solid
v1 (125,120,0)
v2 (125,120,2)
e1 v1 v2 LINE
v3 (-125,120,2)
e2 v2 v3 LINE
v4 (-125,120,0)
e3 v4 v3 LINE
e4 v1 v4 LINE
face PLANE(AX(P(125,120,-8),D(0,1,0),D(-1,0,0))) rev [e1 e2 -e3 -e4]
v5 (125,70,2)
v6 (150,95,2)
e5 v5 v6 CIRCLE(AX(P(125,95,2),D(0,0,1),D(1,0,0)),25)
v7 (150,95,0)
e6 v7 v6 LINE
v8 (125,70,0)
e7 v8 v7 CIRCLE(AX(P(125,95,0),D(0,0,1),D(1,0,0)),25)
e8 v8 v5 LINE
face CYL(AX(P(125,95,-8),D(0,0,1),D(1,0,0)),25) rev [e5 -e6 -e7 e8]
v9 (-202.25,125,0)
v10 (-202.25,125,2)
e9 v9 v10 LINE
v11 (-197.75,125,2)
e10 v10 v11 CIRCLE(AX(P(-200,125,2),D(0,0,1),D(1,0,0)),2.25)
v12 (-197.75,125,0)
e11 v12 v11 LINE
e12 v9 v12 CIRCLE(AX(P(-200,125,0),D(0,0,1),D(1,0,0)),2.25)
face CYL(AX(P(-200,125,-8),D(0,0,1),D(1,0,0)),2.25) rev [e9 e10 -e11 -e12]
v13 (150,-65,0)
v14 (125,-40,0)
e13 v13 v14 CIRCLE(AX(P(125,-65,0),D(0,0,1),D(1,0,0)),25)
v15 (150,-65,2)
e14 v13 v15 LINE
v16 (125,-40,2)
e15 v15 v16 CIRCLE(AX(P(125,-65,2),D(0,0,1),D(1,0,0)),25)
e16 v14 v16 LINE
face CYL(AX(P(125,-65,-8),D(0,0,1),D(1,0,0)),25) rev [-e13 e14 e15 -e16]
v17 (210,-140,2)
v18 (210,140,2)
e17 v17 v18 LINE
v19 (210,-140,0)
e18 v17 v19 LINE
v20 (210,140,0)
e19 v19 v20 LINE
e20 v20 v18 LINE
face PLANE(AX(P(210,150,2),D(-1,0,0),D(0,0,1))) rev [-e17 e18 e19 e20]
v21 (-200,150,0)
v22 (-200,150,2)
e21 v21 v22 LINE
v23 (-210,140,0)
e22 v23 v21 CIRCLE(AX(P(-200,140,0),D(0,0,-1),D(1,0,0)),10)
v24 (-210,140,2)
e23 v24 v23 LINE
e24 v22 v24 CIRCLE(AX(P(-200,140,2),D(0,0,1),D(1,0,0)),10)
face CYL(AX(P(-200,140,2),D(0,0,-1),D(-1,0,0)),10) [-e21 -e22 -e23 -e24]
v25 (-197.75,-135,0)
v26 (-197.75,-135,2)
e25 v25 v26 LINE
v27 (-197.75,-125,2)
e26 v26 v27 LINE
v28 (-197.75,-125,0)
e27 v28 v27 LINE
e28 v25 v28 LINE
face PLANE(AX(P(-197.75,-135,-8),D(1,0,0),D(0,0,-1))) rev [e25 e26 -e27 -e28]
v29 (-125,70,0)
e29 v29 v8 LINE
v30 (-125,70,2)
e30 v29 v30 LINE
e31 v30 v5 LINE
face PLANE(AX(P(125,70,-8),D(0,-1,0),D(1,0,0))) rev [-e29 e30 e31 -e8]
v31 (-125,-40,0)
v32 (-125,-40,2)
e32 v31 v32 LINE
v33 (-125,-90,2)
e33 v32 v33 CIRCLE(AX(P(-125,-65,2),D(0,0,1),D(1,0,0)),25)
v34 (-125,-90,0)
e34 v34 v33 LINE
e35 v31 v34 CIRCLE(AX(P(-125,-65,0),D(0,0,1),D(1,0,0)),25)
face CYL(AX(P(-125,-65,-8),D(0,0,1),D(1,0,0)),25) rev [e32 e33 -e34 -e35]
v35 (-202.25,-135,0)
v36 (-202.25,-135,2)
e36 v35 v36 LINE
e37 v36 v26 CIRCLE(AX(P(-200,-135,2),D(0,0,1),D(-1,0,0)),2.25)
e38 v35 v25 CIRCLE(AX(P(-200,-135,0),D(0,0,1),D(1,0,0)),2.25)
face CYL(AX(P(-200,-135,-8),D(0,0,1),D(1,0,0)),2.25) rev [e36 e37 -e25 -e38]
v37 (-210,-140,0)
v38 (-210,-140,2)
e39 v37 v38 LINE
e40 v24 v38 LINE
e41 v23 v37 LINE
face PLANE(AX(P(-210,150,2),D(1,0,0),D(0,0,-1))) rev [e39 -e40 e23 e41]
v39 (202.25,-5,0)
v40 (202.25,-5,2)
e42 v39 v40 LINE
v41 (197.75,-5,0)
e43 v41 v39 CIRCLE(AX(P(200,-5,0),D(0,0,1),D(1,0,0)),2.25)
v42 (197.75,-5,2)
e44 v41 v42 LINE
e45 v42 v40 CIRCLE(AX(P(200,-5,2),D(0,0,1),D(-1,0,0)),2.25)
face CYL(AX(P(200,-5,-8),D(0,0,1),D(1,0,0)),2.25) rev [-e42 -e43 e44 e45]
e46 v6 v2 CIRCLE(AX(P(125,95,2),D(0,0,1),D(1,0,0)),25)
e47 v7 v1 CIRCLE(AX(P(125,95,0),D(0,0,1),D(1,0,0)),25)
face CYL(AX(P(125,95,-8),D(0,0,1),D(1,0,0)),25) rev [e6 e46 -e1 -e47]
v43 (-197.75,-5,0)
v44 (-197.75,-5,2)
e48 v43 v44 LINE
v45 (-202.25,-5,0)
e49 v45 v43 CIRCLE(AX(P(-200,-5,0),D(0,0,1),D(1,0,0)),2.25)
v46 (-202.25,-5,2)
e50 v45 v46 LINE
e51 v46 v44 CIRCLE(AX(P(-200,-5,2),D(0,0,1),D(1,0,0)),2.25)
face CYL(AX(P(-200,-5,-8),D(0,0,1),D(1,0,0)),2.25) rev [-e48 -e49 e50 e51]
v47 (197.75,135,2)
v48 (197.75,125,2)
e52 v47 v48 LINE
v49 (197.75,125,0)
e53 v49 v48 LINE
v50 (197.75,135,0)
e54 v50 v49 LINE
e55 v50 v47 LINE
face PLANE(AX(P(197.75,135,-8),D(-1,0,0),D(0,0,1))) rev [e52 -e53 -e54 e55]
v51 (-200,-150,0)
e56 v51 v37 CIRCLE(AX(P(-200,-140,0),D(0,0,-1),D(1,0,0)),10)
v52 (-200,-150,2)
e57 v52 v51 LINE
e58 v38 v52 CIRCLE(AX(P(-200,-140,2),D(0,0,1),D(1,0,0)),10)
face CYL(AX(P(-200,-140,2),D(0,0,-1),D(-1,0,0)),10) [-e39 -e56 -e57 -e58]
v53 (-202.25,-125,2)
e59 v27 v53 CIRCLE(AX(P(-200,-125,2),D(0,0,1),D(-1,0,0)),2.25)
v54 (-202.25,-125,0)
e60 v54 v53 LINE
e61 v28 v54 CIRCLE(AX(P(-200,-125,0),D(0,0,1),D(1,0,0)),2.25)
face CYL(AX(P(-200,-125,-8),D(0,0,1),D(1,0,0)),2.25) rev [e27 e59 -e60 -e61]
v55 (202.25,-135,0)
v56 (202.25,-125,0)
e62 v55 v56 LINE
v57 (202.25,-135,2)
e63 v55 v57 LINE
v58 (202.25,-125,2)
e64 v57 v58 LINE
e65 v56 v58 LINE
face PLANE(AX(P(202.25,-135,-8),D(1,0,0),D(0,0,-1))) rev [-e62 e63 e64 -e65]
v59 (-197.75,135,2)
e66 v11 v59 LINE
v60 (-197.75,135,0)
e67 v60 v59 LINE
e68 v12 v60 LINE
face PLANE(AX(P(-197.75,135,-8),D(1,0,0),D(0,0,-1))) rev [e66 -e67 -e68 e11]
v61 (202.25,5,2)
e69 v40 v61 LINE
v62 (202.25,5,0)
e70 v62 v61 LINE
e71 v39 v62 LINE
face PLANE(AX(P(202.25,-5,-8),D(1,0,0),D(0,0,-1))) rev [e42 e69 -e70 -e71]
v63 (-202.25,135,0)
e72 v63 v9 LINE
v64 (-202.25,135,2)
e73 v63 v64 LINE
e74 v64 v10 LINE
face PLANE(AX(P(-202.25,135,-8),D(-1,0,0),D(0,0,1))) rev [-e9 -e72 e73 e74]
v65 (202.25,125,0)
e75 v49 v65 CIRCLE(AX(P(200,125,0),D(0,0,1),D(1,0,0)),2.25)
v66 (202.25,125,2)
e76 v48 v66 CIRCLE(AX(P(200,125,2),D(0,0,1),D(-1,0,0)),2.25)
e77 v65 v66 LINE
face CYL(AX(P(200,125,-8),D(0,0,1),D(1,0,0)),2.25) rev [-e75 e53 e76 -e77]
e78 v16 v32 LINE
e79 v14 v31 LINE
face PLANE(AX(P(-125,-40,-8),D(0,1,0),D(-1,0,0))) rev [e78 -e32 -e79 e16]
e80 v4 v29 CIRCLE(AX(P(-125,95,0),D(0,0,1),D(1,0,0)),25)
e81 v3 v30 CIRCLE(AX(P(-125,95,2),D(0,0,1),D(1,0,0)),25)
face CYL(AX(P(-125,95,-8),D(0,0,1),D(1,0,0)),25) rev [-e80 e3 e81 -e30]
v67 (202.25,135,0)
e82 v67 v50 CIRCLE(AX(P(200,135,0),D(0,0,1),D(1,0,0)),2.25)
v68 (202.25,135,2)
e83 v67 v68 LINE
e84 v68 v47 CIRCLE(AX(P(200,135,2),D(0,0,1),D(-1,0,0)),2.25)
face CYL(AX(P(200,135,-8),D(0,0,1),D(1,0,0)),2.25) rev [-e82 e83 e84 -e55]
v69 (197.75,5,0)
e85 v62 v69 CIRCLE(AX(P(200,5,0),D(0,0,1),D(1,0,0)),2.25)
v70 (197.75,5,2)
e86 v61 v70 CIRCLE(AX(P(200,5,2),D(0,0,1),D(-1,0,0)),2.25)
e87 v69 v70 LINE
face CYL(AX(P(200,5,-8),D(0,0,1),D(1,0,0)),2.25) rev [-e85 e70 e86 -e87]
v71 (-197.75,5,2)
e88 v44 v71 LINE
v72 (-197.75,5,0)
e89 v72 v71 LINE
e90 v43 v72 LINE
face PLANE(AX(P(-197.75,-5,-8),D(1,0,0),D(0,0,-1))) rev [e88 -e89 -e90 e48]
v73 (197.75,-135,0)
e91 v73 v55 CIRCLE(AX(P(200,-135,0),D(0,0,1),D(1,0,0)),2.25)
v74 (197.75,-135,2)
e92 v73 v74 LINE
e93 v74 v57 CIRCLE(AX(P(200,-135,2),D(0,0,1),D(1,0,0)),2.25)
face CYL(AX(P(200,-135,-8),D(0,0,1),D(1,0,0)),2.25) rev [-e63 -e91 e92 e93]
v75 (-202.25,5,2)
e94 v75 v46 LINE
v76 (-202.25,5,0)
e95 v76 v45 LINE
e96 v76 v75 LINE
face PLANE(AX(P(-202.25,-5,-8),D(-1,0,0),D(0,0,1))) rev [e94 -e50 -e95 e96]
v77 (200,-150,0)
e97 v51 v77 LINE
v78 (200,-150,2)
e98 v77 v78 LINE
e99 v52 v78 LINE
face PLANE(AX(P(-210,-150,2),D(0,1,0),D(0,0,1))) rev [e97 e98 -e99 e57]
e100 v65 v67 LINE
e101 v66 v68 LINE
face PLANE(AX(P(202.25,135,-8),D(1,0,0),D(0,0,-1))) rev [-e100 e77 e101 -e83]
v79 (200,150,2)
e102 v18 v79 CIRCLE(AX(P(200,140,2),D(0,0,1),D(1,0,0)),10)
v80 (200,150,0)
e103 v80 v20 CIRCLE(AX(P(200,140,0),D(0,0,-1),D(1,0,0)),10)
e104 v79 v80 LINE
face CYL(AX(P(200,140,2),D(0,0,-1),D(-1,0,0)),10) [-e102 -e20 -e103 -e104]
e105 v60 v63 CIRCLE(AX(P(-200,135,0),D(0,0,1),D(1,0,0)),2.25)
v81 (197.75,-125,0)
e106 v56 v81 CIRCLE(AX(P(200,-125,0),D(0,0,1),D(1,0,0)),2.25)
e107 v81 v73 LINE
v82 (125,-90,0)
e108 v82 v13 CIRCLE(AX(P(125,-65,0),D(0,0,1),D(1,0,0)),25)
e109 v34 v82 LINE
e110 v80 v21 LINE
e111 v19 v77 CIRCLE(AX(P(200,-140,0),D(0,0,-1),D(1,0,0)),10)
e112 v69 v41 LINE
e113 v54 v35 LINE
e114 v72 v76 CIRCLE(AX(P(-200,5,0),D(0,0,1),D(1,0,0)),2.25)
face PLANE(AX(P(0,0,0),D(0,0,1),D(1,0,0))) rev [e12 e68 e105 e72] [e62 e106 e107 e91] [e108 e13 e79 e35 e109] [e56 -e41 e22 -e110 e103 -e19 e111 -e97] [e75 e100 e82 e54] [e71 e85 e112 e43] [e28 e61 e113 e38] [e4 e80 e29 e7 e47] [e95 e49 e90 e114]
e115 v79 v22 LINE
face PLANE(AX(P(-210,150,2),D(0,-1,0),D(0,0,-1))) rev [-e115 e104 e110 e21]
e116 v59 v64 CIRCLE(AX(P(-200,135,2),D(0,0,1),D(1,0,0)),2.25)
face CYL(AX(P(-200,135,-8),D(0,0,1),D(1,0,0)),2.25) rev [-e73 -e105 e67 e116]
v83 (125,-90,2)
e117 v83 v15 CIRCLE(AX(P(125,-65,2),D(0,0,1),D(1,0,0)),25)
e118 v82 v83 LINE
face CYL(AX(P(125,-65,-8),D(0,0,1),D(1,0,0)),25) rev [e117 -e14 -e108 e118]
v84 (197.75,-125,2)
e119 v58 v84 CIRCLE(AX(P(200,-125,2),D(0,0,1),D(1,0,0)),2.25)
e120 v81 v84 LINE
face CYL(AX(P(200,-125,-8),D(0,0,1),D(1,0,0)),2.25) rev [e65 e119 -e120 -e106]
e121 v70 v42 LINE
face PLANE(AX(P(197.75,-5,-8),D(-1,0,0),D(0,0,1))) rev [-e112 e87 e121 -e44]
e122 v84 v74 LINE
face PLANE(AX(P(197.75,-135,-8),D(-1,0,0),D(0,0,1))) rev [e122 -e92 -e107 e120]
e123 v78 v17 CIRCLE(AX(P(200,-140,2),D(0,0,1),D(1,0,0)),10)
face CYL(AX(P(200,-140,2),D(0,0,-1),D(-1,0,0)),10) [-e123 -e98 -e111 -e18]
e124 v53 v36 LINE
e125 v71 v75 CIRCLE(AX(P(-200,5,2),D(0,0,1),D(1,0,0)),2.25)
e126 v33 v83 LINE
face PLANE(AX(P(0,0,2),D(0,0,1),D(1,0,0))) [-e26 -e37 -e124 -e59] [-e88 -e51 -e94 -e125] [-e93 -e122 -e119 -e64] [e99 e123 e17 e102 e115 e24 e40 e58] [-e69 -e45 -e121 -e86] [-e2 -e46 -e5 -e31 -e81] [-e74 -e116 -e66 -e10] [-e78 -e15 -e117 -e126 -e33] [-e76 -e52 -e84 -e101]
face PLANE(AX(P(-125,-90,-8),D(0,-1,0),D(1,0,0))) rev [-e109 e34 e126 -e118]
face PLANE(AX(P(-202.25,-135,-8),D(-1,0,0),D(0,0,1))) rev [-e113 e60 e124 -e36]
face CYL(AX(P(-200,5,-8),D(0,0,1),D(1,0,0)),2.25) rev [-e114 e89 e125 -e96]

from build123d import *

# Parameters (mm, degrees)
SKETCH_1_W          = 420
SKETCH_1_H          = 300
EXTRUDE_1_DEPTH     = 2
HOLE_WIZARD_M4_2_D  = 3.3
CUT_EXTRUDE_1_DEPTH = 10
FILLET_1_R          = 10
CUT_EXTRUDE_2_DEPTH = 10


with BuildPart() as part:
    # 草图1 → 凸台-拉伸1 (new body)
    with BuildSketch(Plane.XY):
        Rectangle(SKETCH_1_W, SKETCH_1_H)
    extrude(amount=EXTRUDE_1_DEPTH)

    # M4 螺纹孔的螺纹孔钻头2 (through all)
    with Locations(Plane.XY.offset(2)):
        with Locations((200, 0), (-200, -130), (-200, 0), (200, -130)):
            Hole(HOLE_WIZARD_M4_2_D / 2)

    # 草图4 → 切除-拉伸1 (cut)
    with BuildSketch(Plane.XY.offset(2)):
        with BuildLine():
            Line((197.75, -135), (197.75, -125))
            ThreePointArc((197.75, -125), (200, -122.75), (202.25, -125))
            Line((202.25, -125), (202.25, -135))
            ThreePointArc((202.25, -135), (200, -137.25), (197.75, -135))
        make_face()
        with BuildLine():
            Line((-197.75, -135), (-197.75, -125))
            ThreePointArc((-197.75, -125), (-200, -122.75), (-202.25, -125))
            Line((-202.25, -125), (-202.25, -135))
            ThreePointArc((-202.25, -135), (-200, -137.25), (-197.75, -135))
        make_face()
        with BuildLine():
            Line((202.25, -5), (202.25, 5))
            ThreePointArc((202.25, 5), (200, 7.25), (197.75, 5))
            Line((197.75, 5), (197.75, -5))
            ThreePointArc((197.75, -5), (200, -7.25), (202.25, -5))
        make_face()
        with BuildLine():
            Line((197.75, 135), (197.75, 125))
            ThreePointArc((197.75, 125), (200, 122.75), (202.25, 125))
            Line((202.25, 125), (202.25, 135))
            ThreePointArc((202.25, 135), (200, 137.25), (197.75, 135))
        make_face()
        with BuildLine():
            Line((-197.75, 135), (-197.75, 125))
            ThreePointArc((-197.75, 125), (-200, 122.75), (-202.25, 125))
            Line((-202.25, 125), (-202.25, 135))
            ThreePointArc((-202.25, 135), (-200, 137.25), (-197.75, 135))
        make_face()
        with BuildLine():
            Line((-202.25, -5), (-202.25, 5))
            ThreePointArc((-202.25, 5), (-200, 7.25), (-197.75, 5))
            Line((-197.75, 5), (-197.75, -5))
            ThreePointArc((-197.75, -5), (-200, -7.25), (-202.25, -5))
        make_face()
    extrude(amount=-CUT_EXTRUDE_1_DEPTH, mode=Mode.SUBTRACT)

    # 圆角1
    fillet_1_edges = [part.edges().sort_by_distance(p)[0] for p in [
        (210, -150, 1),
        (-210, -150, 1),
        (-210, 150, 1),
        (210, 150, 1),
    ]]
    fillet(fillet_1_edges, radius=FILLET_1_R)

    # 草图5 → 切除-拉伸2 (cut)
    with BuildSketch(Plane.XY.offset(2)):
        with BuildLine():
            Line((-125, -40), (125, -40))
            ThreePointArc((125, -40), (150, -65), (125, -90))
            Line((125, -90), (-125, -90))
            ThreePointArc((-125, -90), (-150, -65), (-125, -40))
        make_face()
        with BuildLine():
            Line((125, 70), (-125, 70))
            ThreePointArc((-125, 70), (-150, 95), (-125, 120))
            Line((-125, 120), (125, 120))
            ThreePointArc((125, 120), (150, 95), (125, 70))
        make_face()
    extrude(amount=-CUT_EXTRUDE_2_DEPTH, mode=Mode.SUBTRACT)


solid = part.part
